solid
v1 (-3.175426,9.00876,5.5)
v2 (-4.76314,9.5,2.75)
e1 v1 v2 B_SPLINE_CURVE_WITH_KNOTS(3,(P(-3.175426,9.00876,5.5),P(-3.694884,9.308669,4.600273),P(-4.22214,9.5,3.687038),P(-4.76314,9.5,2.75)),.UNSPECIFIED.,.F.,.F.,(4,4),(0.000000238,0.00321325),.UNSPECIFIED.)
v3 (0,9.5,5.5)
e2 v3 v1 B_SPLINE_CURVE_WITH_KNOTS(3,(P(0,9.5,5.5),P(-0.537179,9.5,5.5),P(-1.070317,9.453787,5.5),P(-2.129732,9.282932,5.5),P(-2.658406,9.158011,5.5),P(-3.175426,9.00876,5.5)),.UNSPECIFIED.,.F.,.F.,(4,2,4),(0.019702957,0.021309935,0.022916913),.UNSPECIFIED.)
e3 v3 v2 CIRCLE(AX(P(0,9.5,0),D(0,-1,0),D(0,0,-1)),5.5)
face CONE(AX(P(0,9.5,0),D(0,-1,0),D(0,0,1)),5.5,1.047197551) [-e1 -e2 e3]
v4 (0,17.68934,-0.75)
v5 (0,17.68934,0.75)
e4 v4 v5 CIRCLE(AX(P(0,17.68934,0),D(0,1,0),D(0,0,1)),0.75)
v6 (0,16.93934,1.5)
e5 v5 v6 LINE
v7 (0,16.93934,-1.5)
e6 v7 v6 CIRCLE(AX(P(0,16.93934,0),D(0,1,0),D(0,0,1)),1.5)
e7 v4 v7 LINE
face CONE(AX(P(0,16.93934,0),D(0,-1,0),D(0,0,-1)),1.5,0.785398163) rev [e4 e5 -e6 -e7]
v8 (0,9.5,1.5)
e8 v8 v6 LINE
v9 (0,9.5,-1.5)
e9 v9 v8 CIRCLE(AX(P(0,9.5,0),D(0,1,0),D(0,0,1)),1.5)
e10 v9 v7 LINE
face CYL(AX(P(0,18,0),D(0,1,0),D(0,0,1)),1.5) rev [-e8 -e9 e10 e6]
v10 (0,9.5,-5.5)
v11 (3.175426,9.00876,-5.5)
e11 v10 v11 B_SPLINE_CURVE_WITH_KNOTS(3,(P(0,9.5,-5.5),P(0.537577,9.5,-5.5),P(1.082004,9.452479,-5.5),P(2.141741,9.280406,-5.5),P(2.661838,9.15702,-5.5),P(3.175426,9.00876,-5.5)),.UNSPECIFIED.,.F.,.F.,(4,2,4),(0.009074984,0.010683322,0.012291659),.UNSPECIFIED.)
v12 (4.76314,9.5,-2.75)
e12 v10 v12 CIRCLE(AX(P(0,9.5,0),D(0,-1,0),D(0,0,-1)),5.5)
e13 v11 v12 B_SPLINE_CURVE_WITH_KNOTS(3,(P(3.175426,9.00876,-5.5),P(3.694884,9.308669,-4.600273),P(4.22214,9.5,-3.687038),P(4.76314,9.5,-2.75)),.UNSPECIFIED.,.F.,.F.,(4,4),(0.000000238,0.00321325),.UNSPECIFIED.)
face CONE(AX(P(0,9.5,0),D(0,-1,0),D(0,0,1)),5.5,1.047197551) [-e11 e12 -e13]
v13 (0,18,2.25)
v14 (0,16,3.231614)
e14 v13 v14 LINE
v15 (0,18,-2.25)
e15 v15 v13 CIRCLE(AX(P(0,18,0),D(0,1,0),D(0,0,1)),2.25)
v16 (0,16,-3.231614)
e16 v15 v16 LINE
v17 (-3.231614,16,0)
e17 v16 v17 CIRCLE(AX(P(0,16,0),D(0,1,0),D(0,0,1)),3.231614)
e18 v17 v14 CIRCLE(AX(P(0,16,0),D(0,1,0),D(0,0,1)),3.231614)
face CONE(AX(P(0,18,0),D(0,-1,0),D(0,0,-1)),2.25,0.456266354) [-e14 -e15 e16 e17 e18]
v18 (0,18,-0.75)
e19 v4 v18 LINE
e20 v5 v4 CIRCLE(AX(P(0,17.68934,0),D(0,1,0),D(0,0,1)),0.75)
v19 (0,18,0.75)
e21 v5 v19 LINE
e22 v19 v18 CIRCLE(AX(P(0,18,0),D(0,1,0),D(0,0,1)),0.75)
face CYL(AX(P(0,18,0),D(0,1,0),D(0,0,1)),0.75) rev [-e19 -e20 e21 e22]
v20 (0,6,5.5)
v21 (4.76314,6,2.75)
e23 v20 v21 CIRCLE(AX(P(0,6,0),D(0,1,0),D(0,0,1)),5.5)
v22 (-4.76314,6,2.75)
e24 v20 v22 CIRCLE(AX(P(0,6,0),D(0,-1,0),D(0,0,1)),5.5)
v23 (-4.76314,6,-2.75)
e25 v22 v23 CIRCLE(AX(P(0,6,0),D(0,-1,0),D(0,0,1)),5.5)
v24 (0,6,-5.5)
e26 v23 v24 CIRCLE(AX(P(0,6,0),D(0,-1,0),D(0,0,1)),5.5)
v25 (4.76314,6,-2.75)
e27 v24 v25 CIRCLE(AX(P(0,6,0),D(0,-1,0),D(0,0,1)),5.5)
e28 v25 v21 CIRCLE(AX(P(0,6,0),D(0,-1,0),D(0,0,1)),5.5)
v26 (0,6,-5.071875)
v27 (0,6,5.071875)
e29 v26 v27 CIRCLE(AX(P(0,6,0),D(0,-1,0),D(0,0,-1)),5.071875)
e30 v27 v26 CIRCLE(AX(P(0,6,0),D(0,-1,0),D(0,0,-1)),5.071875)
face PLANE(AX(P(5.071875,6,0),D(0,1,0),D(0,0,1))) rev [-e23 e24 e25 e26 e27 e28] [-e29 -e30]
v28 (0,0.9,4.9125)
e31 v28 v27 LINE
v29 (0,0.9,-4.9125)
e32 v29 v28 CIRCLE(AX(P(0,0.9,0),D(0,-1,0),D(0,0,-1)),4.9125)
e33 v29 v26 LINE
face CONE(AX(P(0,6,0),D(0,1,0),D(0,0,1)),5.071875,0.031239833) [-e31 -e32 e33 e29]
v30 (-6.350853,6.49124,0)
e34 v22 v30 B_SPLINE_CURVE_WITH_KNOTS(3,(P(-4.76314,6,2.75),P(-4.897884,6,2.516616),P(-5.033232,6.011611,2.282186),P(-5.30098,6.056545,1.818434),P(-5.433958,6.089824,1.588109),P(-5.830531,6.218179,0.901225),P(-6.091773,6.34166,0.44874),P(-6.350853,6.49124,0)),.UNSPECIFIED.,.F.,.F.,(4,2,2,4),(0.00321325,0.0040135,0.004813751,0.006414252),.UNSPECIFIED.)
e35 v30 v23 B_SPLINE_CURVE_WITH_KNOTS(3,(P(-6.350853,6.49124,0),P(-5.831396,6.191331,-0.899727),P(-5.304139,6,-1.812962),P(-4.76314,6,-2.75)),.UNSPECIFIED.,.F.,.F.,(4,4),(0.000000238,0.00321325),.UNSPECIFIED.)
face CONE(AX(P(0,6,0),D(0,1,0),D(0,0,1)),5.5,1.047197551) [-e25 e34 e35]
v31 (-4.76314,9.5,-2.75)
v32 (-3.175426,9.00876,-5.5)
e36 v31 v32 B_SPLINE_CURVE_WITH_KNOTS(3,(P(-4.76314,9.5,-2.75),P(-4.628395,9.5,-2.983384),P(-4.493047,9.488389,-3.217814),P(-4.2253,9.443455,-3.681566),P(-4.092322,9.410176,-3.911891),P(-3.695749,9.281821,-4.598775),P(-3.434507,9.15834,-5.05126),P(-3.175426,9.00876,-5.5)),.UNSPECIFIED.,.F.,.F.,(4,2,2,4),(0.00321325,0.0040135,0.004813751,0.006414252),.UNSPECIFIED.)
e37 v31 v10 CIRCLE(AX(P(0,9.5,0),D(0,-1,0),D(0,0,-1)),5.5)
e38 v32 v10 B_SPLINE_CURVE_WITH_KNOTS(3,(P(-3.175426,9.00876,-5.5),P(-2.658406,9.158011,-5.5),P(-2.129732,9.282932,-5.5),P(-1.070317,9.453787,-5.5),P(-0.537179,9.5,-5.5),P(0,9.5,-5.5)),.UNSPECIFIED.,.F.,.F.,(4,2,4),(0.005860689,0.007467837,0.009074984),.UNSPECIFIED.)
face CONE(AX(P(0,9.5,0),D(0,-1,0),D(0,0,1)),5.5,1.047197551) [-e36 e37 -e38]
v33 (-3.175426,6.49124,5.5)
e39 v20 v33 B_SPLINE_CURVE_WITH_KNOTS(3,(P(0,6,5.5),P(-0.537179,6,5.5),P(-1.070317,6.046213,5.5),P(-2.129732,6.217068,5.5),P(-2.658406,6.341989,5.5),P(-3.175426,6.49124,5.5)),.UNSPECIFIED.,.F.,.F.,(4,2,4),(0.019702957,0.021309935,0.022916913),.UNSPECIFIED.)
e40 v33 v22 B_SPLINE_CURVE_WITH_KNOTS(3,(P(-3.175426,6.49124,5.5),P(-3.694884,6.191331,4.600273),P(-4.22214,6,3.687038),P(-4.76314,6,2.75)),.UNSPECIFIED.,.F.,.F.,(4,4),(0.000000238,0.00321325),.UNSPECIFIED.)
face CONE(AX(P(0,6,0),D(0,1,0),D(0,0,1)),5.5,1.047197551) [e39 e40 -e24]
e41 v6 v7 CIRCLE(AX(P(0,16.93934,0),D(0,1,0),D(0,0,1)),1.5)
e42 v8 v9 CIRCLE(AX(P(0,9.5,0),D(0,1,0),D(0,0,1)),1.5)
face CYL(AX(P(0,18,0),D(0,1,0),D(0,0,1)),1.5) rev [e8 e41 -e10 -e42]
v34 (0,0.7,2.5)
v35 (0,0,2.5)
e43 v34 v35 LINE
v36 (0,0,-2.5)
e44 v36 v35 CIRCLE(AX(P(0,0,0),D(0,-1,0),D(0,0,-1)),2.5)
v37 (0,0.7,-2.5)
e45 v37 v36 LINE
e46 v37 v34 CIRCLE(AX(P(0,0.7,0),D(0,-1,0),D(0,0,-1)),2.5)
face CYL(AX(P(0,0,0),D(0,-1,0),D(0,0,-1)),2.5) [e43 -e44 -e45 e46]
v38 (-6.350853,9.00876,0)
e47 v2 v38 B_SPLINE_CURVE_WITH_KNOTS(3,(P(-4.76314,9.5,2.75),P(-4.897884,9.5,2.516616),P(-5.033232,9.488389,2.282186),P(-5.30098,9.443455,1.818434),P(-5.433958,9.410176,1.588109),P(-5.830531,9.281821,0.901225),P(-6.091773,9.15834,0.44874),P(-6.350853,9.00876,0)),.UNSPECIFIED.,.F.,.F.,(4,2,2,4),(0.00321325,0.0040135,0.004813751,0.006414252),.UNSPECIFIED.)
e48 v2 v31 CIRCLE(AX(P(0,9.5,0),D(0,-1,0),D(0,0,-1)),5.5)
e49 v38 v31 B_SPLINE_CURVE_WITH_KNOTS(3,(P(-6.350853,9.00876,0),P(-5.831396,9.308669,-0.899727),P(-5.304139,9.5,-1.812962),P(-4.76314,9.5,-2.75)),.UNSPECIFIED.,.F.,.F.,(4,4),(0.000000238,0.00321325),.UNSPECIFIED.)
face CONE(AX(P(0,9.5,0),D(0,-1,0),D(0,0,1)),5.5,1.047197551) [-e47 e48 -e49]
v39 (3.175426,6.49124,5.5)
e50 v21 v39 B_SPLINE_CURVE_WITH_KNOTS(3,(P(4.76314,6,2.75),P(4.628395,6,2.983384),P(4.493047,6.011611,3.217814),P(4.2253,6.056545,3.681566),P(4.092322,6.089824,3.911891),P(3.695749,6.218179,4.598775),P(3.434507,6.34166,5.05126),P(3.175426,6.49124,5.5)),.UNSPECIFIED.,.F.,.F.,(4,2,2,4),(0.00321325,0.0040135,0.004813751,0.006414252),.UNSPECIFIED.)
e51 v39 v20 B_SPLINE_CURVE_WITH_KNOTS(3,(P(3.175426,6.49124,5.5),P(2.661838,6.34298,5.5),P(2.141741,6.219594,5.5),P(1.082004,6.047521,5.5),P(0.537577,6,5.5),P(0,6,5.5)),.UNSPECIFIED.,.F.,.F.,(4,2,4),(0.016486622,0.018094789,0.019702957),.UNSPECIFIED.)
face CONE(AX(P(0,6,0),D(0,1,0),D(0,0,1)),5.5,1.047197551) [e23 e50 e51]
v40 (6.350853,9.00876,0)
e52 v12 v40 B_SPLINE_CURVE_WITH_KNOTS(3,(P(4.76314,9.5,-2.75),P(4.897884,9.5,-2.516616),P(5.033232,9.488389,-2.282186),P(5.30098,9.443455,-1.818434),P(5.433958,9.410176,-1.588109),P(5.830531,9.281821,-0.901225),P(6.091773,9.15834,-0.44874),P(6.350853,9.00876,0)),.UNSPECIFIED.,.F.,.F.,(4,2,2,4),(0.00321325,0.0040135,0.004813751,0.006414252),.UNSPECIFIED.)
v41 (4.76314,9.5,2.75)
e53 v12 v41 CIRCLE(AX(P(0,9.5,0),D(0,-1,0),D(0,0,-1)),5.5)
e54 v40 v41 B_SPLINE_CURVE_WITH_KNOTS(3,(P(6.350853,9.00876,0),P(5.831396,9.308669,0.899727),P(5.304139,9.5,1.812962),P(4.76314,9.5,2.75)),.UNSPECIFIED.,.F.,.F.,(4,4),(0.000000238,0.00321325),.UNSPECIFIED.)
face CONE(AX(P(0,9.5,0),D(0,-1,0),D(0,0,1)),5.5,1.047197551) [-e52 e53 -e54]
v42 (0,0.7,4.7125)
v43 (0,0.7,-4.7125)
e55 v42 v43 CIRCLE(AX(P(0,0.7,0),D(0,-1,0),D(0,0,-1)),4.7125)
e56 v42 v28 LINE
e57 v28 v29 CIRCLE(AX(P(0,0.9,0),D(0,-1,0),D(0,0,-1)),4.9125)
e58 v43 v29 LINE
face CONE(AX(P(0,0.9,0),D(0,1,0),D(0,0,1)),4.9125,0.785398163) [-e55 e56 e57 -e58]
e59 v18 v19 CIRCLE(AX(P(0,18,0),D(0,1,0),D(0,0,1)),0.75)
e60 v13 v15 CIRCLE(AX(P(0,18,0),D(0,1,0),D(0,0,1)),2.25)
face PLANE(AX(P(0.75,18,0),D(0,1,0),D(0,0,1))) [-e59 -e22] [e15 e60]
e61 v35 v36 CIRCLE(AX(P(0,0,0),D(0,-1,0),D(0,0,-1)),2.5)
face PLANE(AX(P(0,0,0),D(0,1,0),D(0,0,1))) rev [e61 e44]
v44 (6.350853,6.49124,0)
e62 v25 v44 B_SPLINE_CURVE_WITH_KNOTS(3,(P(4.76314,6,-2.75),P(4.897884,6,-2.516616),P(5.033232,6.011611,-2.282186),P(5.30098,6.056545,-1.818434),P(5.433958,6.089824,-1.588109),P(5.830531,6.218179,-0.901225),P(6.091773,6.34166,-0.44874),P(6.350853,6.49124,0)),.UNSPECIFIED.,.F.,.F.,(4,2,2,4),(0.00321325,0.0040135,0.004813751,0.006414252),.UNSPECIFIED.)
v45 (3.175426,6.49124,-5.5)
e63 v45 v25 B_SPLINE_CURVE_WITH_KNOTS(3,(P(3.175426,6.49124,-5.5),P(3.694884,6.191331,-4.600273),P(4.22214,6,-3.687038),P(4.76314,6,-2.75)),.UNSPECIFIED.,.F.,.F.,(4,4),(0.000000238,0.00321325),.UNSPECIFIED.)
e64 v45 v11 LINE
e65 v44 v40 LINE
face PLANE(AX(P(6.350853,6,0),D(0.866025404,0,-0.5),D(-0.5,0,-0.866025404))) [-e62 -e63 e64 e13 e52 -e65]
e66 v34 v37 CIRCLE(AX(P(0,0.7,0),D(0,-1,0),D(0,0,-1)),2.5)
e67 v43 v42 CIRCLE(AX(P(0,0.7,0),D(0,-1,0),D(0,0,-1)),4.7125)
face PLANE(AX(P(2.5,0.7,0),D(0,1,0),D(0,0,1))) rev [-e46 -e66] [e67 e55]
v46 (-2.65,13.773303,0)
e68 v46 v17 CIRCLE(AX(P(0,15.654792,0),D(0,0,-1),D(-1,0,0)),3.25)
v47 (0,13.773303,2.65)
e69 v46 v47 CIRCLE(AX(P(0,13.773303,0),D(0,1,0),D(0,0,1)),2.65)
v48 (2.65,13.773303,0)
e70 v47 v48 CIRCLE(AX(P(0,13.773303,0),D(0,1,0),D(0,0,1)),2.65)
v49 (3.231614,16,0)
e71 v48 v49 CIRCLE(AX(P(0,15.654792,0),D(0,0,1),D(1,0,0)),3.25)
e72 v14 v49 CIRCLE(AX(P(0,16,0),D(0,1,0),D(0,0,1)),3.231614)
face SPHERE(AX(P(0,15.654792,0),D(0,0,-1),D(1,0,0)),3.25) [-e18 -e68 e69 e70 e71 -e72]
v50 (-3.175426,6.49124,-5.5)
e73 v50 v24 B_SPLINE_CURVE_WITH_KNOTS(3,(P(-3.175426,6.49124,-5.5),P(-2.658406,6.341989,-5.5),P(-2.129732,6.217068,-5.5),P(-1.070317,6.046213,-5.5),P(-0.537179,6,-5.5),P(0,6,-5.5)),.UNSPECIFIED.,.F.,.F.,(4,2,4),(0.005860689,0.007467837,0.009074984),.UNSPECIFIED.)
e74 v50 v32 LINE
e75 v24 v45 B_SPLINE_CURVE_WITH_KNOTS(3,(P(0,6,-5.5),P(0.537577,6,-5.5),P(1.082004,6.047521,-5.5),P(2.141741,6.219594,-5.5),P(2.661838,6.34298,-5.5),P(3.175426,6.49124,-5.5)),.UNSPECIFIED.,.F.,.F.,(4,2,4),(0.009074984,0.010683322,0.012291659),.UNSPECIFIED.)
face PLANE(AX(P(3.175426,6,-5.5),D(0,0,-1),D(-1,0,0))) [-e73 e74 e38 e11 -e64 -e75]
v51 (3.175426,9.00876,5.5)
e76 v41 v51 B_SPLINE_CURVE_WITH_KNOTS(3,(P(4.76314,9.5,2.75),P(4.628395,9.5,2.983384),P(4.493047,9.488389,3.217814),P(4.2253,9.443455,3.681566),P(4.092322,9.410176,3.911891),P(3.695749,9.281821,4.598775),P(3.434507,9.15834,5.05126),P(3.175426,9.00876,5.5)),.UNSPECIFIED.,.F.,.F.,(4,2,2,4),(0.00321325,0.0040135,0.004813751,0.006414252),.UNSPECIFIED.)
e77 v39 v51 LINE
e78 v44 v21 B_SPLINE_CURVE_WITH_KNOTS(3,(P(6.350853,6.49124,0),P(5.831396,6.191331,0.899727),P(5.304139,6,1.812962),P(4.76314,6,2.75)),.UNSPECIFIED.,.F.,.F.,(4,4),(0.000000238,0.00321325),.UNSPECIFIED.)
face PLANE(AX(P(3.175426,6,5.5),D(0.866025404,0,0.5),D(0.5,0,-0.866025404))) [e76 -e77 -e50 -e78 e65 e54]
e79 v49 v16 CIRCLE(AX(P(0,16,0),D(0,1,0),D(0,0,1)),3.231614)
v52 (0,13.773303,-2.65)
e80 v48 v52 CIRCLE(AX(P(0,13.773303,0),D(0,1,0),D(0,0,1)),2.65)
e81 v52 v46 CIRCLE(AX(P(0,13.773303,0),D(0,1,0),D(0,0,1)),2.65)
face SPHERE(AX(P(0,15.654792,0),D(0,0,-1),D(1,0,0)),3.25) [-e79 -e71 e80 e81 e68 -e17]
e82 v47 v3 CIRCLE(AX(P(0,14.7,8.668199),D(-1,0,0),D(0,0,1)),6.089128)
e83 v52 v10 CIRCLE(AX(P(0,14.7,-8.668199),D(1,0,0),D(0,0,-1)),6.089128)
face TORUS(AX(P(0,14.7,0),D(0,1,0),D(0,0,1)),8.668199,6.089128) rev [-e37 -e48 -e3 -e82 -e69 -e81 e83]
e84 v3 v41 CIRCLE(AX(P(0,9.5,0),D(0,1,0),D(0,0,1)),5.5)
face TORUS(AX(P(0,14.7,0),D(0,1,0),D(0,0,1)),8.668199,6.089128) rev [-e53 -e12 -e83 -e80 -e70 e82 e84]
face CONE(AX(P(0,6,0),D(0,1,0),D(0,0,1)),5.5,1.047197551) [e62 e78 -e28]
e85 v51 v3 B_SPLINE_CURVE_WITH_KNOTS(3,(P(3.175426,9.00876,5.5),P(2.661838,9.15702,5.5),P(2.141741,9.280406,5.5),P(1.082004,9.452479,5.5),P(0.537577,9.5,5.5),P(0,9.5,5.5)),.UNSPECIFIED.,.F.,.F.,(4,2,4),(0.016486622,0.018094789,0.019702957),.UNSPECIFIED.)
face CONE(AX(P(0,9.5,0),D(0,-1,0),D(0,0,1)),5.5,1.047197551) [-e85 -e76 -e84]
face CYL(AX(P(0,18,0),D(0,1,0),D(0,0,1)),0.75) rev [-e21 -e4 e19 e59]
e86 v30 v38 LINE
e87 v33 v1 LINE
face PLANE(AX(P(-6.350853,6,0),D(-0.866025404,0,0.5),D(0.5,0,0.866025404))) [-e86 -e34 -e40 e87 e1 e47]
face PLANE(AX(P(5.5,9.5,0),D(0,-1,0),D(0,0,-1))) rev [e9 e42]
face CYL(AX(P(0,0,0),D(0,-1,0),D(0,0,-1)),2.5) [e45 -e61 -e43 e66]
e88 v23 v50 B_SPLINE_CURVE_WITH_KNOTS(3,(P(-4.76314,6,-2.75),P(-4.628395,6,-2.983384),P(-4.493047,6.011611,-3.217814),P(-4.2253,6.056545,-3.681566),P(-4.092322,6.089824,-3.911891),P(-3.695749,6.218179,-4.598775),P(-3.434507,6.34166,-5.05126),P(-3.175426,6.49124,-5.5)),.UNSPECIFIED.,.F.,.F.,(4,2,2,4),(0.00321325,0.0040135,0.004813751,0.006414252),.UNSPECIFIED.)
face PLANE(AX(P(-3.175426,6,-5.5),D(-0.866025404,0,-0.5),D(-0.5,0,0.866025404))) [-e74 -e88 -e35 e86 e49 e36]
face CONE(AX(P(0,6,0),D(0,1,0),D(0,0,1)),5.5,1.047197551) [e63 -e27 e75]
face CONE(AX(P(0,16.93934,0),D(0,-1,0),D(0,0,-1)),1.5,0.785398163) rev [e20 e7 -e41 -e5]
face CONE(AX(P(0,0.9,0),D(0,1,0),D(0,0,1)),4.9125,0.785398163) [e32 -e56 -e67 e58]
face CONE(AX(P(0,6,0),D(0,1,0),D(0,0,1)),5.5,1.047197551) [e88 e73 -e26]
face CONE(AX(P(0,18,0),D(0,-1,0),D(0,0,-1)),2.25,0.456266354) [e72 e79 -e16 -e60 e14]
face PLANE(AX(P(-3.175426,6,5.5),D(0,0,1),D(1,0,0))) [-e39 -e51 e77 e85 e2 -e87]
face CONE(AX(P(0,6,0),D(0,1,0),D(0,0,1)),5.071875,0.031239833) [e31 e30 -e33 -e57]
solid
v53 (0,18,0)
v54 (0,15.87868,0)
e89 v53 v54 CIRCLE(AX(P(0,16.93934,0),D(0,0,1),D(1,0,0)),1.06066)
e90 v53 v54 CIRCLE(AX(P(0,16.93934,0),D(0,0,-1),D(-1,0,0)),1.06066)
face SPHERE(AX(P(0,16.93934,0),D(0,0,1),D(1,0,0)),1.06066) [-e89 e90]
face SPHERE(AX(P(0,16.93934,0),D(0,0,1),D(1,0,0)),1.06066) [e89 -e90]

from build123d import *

# Parameters (mm, degrees)
EXTRUDE_START        = 9.5
EXTRUDE_1_DEPTH      = 3.5
CUT_EXTRUDE_START    = 9.5
SKETCH_3_3_OUTSIDE_W = 30.686
SKETCH_3_3_OUTSIDE_H = 28.984
SKETCH_3_3_OUTSIDE_R = 5.5
CUT_EXTRUDE_1_DEPTH  = 3.5
CUT_EXTRUDE_1_DRAFT  = -60
CUT_EXTRUDE_START_2  = 6
SKETCH_3_4_OUTSIDE_W = 30.686
SKETCH_3_4_OUTSIDE_H = 28.984
SKETCH_3_4_OUTSIDE_R = 5.5
CUT_EXTRUDE_2_DEPTH  = 3.5
CUT_EXTRUDE_2_DRAFT  = 60


with BuildPart() as part:
    # 草图2 → 旋转1 (revolve)
    with BuildSketch(Plane.XY, mode=Mode.PRIVATE) as revolve_1_sk:
        Polygon((0, 0), (-2.5, 0), (-2.5, 0.7), (-4.7125, 0.7), (-4.9125, 0.9), (-5.071875, 6), (-5.5, 6), (-5.5, 9.5), (0, 9.5), align=None)
    revolve(revolve_1_sk.sketch.rotate(Axis((0, 0, 0), (0, 1, 0)), 270), axis=Axis((0, 0, 0), (0, 1, 0)))

    # 草图3 → 凸台-拉伸1 (add)
    with BuildSketch(Plane(origin=(0, 0, 0), x_dir=(1, 0, 0), z_dir=(0, 1, 0)).offset(EXTRUDE_START)):
        Polygon((6.350852961, 0), (3.175426481, 5.5), (-3.175426481, 5.5), (-6.350852961, 0), (-3.175426481, -5.5), (3.175426481, -5.5), align=None)
    extrude(amount=-EXTRUDE_1_DEPTH)


with BuildPart() as cut_extrude_1_tool:
    # 草图3<3> outside → 切除-拉伸1 (with draft: the straight prism first)
    with BuildSketch(Plane(origin=(0, 0, 0), x_dir=(1, 0, 0), z_dir=(0, 1, 0)).offset(CUT_EXTRUDE_START)):
        Rectangle(SKETCH_3_3_OUTSIDE_W, SKETCH_3_3_OUTSIDE_H)
        Circle(SKETCH_3_3_OUTSIDE_R, mode=Mode.SUBTRACT)
    extrude(amount=-CUT_EXTRUDE_1_DEPTH)
    # 切除-拉伸1: the draft: its side faces are tilted about the plane it starts from
    cut_extrude_1_sides = [cut_extrude_1_tool.faces().sort_by_distance(p)[0] for p in [
        (0, 7.75, 14.492),
        (15.343, 7.75, 0),
        (0, 7.75, -14.492),
        (-15.343, 7.75, 0),
        (-5.5, 7.75, 0),
    ]]
    draft(cut_extrude_1_sides, Plane(origin=(0, 0, 0), x_dir=(1, 0, 0), z_dir=(0, 1, 0)).offset(CUT_EXTRUDE_START), CUT_EXTRUDE_1_DRAFT)


with BuildPart() as part_1:
    add(part.part)

    # 切除-拉伸1: cut by cut_extrude_1_tool
    add(cut_extrude_1_tool.part, mode=Mode.SUBTRACT)


with BuildPart() as cut_extrude_2_tool:
    # 草图3<4> outside → 切除-拉伸2 (with draft: the straight prism first)
    with BuildSketch(Plane(origin=(0, 0, 0), x_dir=(1, 0, 0), z_dir=(0, 1, 0)).offset(CUT_EXTRUDE_START_2)):
        Rectangle(SKETCH_3_4_OUTSIDE_W, SKETCH_3_4_OUTSIDE_H)
        Circle(SKETCH_3_4_OUTSIDE_R, mode=Mode.SUBTRACT)
    extrude(amount=CUT_EXTRUDE_2_DEPTH)
    # 切除-拉伸2: the draft: its side faces are tilted about the plane it starts from
    cut_extrude_2_sides = [cut_extrude_2_tool.faces().sort_by_distance(p)[0] for p in [
        (0, 7.75, 14.492),
        (15.343, 7.75, 0),
        (0, 7.75, -14.492),
        (-15.343, 7.75, 0),
        (-5.5, 7.75, 0),
    ]]
    draft(cut_extrude_2_sides, Plane(origin=(0, 0, 0), x_dir=(1, 0, 0), z_dir=(0, 1, 0)).offset(CUT_EXTRUDE_START_2), CUT_EXTRUDE_2_DRAFT)


with BuildPart() as part_2:
    add(part_1.part)

    # 切除-拉伸2: cut by cut_extrude_2_tool
    add(cut_extrude_2_tool.part, mode=Mode.SUBTRACT)

    # 草图4 → 旋转2 (revolve)
    with BuildSketch(Plane.XY, mode=Mode.PRIVATE) as revolve_2_sk:
        with BuildLine():
            Line((-0.75, 18), (-2.25, 18))
            Line((-2.25, 18), (-3.231614383, 16))
            ThreePointArc((-3.231614383, 16), (-3.144501778, 14.833446537), (-2.65, 13.773303348))
            ThreePointArc((-2.65, 13.773303348), (-3.602356761, 11.321431077), (-5.5, 9.5))
            Line((-5.5, 9.5), (-1.5, 9.5))
            Line((-1.5, 9.5), (-1.5, 16.939339828))
            Line((-1.5, 16.939339828), (-0.75, 17.689339828))
            Line((-0.75, 17.689339828), (-0.75, 18))
        make_face()
    revolve(revolve_2_sk.sketch.rotate(Axis((0, 18, 0), (0, -1, 0)), 270), axis=Axis((0, 18, 0), (0, -1, 0)))


with BuildPart() as body_2:
    # 草图5 → 旋转3 (revolve)
    with BuildSketch(Plane.XY):
        with BuildLine():
            Line((0, 15.878679656), (0, 18))
            ThreePointArc((0, 18), (-1.060660172, 16.939339828), (0, 15.878679656))
        make_face()
    revolve(axis=Axis((0, 0, 0), (0, 1, 0)))


solid = Compound([part_2.part, body_2.part])
